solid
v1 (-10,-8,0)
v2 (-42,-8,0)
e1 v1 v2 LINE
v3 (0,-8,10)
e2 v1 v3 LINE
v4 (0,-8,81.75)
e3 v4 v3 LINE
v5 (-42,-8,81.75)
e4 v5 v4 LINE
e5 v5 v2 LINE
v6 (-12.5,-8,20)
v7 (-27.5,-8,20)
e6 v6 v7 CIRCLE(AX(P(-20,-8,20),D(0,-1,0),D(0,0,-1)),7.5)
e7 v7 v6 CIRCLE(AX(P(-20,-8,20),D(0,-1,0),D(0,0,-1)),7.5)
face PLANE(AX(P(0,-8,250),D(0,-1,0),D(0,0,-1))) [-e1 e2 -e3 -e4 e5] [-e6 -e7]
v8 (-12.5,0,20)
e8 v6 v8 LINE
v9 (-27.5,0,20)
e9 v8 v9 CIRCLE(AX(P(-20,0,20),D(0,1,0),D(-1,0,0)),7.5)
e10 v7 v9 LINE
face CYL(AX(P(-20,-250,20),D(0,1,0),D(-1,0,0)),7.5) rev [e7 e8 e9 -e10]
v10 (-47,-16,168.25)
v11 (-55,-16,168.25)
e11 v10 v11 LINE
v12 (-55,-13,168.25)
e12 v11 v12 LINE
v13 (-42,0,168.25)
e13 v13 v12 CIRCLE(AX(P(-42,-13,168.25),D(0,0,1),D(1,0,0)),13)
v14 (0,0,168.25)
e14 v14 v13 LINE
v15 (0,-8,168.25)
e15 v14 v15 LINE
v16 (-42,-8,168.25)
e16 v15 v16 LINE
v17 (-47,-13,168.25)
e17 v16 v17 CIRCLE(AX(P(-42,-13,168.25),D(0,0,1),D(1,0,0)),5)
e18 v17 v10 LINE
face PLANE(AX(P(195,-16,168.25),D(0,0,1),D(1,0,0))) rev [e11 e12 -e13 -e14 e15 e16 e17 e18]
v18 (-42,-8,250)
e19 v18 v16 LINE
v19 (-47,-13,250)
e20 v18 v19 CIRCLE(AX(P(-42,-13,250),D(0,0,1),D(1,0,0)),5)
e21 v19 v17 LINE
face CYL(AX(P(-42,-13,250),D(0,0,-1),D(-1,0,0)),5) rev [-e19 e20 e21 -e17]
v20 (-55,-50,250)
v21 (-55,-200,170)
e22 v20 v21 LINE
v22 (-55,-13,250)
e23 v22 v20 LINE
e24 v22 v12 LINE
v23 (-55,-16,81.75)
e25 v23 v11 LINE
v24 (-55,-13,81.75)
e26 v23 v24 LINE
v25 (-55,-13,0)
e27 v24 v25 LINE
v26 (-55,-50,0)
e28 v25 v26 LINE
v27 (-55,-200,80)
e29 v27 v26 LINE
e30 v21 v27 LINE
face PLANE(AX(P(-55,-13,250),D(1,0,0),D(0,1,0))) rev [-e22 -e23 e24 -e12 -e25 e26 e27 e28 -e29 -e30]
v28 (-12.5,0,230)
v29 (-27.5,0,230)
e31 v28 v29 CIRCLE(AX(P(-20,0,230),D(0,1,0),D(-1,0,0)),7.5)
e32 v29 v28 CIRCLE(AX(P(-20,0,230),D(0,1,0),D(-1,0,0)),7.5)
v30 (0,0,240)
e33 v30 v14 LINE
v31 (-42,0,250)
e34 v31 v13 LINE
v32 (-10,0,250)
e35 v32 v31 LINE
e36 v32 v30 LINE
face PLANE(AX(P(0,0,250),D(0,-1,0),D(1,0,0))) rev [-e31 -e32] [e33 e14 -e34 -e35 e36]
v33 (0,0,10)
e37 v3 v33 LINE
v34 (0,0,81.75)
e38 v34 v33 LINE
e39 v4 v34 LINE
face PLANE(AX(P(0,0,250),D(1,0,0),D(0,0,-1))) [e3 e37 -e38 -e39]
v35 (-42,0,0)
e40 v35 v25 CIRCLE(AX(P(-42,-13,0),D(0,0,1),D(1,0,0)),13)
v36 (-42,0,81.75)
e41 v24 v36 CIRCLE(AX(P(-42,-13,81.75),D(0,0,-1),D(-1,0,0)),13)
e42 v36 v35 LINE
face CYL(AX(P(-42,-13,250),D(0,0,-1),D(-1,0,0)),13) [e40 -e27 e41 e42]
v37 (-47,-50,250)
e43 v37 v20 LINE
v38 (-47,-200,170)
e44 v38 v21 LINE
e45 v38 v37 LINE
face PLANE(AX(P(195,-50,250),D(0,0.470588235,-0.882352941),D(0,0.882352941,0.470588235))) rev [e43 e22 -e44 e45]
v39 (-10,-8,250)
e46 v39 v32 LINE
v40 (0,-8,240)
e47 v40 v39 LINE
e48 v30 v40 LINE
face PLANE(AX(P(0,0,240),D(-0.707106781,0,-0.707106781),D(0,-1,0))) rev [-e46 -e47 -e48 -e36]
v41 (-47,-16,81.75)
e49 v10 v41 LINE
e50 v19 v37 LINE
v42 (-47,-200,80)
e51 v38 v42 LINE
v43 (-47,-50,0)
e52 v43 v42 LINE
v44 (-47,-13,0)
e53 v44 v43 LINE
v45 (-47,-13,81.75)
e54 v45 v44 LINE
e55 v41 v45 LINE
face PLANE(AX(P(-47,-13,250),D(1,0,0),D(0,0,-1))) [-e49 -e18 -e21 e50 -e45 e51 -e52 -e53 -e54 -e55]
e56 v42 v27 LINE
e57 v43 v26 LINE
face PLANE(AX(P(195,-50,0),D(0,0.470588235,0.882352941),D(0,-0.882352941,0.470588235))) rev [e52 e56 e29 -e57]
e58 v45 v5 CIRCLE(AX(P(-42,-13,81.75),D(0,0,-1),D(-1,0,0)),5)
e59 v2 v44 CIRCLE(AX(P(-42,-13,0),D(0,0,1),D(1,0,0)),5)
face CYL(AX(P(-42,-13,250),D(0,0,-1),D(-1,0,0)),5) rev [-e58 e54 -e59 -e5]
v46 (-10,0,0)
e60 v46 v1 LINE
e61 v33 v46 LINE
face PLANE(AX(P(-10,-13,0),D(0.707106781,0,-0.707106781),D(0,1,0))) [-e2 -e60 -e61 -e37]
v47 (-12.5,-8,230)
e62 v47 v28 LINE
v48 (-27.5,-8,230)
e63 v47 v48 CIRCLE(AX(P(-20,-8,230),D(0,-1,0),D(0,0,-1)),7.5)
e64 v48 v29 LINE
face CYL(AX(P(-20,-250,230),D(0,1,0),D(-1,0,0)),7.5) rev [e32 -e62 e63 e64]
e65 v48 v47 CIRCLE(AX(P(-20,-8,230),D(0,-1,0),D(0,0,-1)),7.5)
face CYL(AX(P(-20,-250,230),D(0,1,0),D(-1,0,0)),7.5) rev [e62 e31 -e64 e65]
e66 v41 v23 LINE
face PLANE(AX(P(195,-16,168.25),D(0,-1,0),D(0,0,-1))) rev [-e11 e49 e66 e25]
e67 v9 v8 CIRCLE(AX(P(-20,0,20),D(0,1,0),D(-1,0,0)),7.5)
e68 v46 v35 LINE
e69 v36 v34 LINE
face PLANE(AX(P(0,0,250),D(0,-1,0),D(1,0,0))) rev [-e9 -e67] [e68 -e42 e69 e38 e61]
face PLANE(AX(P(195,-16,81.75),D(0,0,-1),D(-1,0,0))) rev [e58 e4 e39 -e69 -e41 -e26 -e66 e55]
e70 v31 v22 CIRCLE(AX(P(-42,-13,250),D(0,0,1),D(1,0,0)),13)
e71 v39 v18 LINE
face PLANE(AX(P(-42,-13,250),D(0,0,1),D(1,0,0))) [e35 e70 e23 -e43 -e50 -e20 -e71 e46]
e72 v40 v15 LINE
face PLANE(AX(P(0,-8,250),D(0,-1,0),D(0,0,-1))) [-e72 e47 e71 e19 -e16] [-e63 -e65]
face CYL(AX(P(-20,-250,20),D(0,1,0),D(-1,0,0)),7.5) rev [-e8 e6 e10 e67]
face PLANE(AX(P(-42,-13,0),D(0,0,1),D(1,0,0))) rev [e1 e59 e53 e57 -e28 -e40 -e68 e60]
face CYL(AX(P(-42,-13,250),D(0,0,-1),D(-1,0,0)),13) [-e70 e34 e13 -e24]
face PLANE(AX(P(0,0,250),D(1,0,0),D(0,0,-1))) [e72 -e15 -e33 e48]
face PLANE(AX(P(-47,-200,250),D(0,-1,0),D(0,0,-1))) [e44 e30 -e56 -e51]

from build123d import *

# Parameters (mm, degrees)
BOSS_EXTRUDE1_DEPTH = 250
SKETCH2_W           = 86.5
SKETCH2_H           = 88.492592909
CUT_EXTRUDE1_DEPTH  = 250
SKETCH3_R           = 7.5
CUT_EXTRUDE2_DEPTH  = 250
CHAMFER1_SIZE       = 10


with BuildPart() as part:
    # Sketch1 → Boss-Extrude1 (new body)
    with BuildSketch(Plane.XY):
        with BuildLine():
            Line((0, 0), (-42, 0))
            ThreePointArc((-42, 0), (-51.192388155, -3.807611845), (-55, -13))
            Line((-55, -13), (-55, -200))
            Line((-55, -200), (-47, -200))
            Line((-47, -200), (-47, -13))
            ThreePointArc((-47, -13), (-45.535533906, -9.464466094), (-42, -8))
            Line((-42, -8), (0, -8))
            Line((0, -8), (0, 0))
        make_face()
    extrude(amount=BOSS_EXTRUDE1_DEPTH)

    # Sketch2 → Cut-Extrude1 (cut)
    with BuildSketch(Plane.ZY.offset(55)):
        Polygon((0, -50), (80, -200), (0, -200), align=None)
        Polygon((170, -200), (250, -200), (250, -50), align=None)
        with Locations((125, 28.246296455)):
            Rectangle(SKETCH2_W, SKETCH2_H)
    extrude(amount=-CUT_EXTRUDE1_DEPTH, mode=Mode.SUBTRACT)

    # Sketch3 → Cut-Extrude2 (cut)
    with BuildSketch(Plane(origin=(0, 0, 0), x_dir=(1, 0, 0), z_dir=(0, 1, 0))):
        with Locations(Location((-20, -20, 0), (0, 0, 180))):
            Circle(SKETCH3_R)
        with Locations(Location((-20, -230, 0), (0, 0, 180))):
            Circle(SKETCH3_R)
    extrude(amount=-CUT_EXTRUDE2_DEPTH, mode=Mode.SUBTRACT)

    # Chamfer1
    chamfer1_edges = [part.edges().sort_by_distance(p)[0] for p in [
        (0, -4, 250),
        (0, -4, 0),
    ]]
    chamfer(chamfer1_edges, length=CHAMFER1_SIZE)


solid = part.part
